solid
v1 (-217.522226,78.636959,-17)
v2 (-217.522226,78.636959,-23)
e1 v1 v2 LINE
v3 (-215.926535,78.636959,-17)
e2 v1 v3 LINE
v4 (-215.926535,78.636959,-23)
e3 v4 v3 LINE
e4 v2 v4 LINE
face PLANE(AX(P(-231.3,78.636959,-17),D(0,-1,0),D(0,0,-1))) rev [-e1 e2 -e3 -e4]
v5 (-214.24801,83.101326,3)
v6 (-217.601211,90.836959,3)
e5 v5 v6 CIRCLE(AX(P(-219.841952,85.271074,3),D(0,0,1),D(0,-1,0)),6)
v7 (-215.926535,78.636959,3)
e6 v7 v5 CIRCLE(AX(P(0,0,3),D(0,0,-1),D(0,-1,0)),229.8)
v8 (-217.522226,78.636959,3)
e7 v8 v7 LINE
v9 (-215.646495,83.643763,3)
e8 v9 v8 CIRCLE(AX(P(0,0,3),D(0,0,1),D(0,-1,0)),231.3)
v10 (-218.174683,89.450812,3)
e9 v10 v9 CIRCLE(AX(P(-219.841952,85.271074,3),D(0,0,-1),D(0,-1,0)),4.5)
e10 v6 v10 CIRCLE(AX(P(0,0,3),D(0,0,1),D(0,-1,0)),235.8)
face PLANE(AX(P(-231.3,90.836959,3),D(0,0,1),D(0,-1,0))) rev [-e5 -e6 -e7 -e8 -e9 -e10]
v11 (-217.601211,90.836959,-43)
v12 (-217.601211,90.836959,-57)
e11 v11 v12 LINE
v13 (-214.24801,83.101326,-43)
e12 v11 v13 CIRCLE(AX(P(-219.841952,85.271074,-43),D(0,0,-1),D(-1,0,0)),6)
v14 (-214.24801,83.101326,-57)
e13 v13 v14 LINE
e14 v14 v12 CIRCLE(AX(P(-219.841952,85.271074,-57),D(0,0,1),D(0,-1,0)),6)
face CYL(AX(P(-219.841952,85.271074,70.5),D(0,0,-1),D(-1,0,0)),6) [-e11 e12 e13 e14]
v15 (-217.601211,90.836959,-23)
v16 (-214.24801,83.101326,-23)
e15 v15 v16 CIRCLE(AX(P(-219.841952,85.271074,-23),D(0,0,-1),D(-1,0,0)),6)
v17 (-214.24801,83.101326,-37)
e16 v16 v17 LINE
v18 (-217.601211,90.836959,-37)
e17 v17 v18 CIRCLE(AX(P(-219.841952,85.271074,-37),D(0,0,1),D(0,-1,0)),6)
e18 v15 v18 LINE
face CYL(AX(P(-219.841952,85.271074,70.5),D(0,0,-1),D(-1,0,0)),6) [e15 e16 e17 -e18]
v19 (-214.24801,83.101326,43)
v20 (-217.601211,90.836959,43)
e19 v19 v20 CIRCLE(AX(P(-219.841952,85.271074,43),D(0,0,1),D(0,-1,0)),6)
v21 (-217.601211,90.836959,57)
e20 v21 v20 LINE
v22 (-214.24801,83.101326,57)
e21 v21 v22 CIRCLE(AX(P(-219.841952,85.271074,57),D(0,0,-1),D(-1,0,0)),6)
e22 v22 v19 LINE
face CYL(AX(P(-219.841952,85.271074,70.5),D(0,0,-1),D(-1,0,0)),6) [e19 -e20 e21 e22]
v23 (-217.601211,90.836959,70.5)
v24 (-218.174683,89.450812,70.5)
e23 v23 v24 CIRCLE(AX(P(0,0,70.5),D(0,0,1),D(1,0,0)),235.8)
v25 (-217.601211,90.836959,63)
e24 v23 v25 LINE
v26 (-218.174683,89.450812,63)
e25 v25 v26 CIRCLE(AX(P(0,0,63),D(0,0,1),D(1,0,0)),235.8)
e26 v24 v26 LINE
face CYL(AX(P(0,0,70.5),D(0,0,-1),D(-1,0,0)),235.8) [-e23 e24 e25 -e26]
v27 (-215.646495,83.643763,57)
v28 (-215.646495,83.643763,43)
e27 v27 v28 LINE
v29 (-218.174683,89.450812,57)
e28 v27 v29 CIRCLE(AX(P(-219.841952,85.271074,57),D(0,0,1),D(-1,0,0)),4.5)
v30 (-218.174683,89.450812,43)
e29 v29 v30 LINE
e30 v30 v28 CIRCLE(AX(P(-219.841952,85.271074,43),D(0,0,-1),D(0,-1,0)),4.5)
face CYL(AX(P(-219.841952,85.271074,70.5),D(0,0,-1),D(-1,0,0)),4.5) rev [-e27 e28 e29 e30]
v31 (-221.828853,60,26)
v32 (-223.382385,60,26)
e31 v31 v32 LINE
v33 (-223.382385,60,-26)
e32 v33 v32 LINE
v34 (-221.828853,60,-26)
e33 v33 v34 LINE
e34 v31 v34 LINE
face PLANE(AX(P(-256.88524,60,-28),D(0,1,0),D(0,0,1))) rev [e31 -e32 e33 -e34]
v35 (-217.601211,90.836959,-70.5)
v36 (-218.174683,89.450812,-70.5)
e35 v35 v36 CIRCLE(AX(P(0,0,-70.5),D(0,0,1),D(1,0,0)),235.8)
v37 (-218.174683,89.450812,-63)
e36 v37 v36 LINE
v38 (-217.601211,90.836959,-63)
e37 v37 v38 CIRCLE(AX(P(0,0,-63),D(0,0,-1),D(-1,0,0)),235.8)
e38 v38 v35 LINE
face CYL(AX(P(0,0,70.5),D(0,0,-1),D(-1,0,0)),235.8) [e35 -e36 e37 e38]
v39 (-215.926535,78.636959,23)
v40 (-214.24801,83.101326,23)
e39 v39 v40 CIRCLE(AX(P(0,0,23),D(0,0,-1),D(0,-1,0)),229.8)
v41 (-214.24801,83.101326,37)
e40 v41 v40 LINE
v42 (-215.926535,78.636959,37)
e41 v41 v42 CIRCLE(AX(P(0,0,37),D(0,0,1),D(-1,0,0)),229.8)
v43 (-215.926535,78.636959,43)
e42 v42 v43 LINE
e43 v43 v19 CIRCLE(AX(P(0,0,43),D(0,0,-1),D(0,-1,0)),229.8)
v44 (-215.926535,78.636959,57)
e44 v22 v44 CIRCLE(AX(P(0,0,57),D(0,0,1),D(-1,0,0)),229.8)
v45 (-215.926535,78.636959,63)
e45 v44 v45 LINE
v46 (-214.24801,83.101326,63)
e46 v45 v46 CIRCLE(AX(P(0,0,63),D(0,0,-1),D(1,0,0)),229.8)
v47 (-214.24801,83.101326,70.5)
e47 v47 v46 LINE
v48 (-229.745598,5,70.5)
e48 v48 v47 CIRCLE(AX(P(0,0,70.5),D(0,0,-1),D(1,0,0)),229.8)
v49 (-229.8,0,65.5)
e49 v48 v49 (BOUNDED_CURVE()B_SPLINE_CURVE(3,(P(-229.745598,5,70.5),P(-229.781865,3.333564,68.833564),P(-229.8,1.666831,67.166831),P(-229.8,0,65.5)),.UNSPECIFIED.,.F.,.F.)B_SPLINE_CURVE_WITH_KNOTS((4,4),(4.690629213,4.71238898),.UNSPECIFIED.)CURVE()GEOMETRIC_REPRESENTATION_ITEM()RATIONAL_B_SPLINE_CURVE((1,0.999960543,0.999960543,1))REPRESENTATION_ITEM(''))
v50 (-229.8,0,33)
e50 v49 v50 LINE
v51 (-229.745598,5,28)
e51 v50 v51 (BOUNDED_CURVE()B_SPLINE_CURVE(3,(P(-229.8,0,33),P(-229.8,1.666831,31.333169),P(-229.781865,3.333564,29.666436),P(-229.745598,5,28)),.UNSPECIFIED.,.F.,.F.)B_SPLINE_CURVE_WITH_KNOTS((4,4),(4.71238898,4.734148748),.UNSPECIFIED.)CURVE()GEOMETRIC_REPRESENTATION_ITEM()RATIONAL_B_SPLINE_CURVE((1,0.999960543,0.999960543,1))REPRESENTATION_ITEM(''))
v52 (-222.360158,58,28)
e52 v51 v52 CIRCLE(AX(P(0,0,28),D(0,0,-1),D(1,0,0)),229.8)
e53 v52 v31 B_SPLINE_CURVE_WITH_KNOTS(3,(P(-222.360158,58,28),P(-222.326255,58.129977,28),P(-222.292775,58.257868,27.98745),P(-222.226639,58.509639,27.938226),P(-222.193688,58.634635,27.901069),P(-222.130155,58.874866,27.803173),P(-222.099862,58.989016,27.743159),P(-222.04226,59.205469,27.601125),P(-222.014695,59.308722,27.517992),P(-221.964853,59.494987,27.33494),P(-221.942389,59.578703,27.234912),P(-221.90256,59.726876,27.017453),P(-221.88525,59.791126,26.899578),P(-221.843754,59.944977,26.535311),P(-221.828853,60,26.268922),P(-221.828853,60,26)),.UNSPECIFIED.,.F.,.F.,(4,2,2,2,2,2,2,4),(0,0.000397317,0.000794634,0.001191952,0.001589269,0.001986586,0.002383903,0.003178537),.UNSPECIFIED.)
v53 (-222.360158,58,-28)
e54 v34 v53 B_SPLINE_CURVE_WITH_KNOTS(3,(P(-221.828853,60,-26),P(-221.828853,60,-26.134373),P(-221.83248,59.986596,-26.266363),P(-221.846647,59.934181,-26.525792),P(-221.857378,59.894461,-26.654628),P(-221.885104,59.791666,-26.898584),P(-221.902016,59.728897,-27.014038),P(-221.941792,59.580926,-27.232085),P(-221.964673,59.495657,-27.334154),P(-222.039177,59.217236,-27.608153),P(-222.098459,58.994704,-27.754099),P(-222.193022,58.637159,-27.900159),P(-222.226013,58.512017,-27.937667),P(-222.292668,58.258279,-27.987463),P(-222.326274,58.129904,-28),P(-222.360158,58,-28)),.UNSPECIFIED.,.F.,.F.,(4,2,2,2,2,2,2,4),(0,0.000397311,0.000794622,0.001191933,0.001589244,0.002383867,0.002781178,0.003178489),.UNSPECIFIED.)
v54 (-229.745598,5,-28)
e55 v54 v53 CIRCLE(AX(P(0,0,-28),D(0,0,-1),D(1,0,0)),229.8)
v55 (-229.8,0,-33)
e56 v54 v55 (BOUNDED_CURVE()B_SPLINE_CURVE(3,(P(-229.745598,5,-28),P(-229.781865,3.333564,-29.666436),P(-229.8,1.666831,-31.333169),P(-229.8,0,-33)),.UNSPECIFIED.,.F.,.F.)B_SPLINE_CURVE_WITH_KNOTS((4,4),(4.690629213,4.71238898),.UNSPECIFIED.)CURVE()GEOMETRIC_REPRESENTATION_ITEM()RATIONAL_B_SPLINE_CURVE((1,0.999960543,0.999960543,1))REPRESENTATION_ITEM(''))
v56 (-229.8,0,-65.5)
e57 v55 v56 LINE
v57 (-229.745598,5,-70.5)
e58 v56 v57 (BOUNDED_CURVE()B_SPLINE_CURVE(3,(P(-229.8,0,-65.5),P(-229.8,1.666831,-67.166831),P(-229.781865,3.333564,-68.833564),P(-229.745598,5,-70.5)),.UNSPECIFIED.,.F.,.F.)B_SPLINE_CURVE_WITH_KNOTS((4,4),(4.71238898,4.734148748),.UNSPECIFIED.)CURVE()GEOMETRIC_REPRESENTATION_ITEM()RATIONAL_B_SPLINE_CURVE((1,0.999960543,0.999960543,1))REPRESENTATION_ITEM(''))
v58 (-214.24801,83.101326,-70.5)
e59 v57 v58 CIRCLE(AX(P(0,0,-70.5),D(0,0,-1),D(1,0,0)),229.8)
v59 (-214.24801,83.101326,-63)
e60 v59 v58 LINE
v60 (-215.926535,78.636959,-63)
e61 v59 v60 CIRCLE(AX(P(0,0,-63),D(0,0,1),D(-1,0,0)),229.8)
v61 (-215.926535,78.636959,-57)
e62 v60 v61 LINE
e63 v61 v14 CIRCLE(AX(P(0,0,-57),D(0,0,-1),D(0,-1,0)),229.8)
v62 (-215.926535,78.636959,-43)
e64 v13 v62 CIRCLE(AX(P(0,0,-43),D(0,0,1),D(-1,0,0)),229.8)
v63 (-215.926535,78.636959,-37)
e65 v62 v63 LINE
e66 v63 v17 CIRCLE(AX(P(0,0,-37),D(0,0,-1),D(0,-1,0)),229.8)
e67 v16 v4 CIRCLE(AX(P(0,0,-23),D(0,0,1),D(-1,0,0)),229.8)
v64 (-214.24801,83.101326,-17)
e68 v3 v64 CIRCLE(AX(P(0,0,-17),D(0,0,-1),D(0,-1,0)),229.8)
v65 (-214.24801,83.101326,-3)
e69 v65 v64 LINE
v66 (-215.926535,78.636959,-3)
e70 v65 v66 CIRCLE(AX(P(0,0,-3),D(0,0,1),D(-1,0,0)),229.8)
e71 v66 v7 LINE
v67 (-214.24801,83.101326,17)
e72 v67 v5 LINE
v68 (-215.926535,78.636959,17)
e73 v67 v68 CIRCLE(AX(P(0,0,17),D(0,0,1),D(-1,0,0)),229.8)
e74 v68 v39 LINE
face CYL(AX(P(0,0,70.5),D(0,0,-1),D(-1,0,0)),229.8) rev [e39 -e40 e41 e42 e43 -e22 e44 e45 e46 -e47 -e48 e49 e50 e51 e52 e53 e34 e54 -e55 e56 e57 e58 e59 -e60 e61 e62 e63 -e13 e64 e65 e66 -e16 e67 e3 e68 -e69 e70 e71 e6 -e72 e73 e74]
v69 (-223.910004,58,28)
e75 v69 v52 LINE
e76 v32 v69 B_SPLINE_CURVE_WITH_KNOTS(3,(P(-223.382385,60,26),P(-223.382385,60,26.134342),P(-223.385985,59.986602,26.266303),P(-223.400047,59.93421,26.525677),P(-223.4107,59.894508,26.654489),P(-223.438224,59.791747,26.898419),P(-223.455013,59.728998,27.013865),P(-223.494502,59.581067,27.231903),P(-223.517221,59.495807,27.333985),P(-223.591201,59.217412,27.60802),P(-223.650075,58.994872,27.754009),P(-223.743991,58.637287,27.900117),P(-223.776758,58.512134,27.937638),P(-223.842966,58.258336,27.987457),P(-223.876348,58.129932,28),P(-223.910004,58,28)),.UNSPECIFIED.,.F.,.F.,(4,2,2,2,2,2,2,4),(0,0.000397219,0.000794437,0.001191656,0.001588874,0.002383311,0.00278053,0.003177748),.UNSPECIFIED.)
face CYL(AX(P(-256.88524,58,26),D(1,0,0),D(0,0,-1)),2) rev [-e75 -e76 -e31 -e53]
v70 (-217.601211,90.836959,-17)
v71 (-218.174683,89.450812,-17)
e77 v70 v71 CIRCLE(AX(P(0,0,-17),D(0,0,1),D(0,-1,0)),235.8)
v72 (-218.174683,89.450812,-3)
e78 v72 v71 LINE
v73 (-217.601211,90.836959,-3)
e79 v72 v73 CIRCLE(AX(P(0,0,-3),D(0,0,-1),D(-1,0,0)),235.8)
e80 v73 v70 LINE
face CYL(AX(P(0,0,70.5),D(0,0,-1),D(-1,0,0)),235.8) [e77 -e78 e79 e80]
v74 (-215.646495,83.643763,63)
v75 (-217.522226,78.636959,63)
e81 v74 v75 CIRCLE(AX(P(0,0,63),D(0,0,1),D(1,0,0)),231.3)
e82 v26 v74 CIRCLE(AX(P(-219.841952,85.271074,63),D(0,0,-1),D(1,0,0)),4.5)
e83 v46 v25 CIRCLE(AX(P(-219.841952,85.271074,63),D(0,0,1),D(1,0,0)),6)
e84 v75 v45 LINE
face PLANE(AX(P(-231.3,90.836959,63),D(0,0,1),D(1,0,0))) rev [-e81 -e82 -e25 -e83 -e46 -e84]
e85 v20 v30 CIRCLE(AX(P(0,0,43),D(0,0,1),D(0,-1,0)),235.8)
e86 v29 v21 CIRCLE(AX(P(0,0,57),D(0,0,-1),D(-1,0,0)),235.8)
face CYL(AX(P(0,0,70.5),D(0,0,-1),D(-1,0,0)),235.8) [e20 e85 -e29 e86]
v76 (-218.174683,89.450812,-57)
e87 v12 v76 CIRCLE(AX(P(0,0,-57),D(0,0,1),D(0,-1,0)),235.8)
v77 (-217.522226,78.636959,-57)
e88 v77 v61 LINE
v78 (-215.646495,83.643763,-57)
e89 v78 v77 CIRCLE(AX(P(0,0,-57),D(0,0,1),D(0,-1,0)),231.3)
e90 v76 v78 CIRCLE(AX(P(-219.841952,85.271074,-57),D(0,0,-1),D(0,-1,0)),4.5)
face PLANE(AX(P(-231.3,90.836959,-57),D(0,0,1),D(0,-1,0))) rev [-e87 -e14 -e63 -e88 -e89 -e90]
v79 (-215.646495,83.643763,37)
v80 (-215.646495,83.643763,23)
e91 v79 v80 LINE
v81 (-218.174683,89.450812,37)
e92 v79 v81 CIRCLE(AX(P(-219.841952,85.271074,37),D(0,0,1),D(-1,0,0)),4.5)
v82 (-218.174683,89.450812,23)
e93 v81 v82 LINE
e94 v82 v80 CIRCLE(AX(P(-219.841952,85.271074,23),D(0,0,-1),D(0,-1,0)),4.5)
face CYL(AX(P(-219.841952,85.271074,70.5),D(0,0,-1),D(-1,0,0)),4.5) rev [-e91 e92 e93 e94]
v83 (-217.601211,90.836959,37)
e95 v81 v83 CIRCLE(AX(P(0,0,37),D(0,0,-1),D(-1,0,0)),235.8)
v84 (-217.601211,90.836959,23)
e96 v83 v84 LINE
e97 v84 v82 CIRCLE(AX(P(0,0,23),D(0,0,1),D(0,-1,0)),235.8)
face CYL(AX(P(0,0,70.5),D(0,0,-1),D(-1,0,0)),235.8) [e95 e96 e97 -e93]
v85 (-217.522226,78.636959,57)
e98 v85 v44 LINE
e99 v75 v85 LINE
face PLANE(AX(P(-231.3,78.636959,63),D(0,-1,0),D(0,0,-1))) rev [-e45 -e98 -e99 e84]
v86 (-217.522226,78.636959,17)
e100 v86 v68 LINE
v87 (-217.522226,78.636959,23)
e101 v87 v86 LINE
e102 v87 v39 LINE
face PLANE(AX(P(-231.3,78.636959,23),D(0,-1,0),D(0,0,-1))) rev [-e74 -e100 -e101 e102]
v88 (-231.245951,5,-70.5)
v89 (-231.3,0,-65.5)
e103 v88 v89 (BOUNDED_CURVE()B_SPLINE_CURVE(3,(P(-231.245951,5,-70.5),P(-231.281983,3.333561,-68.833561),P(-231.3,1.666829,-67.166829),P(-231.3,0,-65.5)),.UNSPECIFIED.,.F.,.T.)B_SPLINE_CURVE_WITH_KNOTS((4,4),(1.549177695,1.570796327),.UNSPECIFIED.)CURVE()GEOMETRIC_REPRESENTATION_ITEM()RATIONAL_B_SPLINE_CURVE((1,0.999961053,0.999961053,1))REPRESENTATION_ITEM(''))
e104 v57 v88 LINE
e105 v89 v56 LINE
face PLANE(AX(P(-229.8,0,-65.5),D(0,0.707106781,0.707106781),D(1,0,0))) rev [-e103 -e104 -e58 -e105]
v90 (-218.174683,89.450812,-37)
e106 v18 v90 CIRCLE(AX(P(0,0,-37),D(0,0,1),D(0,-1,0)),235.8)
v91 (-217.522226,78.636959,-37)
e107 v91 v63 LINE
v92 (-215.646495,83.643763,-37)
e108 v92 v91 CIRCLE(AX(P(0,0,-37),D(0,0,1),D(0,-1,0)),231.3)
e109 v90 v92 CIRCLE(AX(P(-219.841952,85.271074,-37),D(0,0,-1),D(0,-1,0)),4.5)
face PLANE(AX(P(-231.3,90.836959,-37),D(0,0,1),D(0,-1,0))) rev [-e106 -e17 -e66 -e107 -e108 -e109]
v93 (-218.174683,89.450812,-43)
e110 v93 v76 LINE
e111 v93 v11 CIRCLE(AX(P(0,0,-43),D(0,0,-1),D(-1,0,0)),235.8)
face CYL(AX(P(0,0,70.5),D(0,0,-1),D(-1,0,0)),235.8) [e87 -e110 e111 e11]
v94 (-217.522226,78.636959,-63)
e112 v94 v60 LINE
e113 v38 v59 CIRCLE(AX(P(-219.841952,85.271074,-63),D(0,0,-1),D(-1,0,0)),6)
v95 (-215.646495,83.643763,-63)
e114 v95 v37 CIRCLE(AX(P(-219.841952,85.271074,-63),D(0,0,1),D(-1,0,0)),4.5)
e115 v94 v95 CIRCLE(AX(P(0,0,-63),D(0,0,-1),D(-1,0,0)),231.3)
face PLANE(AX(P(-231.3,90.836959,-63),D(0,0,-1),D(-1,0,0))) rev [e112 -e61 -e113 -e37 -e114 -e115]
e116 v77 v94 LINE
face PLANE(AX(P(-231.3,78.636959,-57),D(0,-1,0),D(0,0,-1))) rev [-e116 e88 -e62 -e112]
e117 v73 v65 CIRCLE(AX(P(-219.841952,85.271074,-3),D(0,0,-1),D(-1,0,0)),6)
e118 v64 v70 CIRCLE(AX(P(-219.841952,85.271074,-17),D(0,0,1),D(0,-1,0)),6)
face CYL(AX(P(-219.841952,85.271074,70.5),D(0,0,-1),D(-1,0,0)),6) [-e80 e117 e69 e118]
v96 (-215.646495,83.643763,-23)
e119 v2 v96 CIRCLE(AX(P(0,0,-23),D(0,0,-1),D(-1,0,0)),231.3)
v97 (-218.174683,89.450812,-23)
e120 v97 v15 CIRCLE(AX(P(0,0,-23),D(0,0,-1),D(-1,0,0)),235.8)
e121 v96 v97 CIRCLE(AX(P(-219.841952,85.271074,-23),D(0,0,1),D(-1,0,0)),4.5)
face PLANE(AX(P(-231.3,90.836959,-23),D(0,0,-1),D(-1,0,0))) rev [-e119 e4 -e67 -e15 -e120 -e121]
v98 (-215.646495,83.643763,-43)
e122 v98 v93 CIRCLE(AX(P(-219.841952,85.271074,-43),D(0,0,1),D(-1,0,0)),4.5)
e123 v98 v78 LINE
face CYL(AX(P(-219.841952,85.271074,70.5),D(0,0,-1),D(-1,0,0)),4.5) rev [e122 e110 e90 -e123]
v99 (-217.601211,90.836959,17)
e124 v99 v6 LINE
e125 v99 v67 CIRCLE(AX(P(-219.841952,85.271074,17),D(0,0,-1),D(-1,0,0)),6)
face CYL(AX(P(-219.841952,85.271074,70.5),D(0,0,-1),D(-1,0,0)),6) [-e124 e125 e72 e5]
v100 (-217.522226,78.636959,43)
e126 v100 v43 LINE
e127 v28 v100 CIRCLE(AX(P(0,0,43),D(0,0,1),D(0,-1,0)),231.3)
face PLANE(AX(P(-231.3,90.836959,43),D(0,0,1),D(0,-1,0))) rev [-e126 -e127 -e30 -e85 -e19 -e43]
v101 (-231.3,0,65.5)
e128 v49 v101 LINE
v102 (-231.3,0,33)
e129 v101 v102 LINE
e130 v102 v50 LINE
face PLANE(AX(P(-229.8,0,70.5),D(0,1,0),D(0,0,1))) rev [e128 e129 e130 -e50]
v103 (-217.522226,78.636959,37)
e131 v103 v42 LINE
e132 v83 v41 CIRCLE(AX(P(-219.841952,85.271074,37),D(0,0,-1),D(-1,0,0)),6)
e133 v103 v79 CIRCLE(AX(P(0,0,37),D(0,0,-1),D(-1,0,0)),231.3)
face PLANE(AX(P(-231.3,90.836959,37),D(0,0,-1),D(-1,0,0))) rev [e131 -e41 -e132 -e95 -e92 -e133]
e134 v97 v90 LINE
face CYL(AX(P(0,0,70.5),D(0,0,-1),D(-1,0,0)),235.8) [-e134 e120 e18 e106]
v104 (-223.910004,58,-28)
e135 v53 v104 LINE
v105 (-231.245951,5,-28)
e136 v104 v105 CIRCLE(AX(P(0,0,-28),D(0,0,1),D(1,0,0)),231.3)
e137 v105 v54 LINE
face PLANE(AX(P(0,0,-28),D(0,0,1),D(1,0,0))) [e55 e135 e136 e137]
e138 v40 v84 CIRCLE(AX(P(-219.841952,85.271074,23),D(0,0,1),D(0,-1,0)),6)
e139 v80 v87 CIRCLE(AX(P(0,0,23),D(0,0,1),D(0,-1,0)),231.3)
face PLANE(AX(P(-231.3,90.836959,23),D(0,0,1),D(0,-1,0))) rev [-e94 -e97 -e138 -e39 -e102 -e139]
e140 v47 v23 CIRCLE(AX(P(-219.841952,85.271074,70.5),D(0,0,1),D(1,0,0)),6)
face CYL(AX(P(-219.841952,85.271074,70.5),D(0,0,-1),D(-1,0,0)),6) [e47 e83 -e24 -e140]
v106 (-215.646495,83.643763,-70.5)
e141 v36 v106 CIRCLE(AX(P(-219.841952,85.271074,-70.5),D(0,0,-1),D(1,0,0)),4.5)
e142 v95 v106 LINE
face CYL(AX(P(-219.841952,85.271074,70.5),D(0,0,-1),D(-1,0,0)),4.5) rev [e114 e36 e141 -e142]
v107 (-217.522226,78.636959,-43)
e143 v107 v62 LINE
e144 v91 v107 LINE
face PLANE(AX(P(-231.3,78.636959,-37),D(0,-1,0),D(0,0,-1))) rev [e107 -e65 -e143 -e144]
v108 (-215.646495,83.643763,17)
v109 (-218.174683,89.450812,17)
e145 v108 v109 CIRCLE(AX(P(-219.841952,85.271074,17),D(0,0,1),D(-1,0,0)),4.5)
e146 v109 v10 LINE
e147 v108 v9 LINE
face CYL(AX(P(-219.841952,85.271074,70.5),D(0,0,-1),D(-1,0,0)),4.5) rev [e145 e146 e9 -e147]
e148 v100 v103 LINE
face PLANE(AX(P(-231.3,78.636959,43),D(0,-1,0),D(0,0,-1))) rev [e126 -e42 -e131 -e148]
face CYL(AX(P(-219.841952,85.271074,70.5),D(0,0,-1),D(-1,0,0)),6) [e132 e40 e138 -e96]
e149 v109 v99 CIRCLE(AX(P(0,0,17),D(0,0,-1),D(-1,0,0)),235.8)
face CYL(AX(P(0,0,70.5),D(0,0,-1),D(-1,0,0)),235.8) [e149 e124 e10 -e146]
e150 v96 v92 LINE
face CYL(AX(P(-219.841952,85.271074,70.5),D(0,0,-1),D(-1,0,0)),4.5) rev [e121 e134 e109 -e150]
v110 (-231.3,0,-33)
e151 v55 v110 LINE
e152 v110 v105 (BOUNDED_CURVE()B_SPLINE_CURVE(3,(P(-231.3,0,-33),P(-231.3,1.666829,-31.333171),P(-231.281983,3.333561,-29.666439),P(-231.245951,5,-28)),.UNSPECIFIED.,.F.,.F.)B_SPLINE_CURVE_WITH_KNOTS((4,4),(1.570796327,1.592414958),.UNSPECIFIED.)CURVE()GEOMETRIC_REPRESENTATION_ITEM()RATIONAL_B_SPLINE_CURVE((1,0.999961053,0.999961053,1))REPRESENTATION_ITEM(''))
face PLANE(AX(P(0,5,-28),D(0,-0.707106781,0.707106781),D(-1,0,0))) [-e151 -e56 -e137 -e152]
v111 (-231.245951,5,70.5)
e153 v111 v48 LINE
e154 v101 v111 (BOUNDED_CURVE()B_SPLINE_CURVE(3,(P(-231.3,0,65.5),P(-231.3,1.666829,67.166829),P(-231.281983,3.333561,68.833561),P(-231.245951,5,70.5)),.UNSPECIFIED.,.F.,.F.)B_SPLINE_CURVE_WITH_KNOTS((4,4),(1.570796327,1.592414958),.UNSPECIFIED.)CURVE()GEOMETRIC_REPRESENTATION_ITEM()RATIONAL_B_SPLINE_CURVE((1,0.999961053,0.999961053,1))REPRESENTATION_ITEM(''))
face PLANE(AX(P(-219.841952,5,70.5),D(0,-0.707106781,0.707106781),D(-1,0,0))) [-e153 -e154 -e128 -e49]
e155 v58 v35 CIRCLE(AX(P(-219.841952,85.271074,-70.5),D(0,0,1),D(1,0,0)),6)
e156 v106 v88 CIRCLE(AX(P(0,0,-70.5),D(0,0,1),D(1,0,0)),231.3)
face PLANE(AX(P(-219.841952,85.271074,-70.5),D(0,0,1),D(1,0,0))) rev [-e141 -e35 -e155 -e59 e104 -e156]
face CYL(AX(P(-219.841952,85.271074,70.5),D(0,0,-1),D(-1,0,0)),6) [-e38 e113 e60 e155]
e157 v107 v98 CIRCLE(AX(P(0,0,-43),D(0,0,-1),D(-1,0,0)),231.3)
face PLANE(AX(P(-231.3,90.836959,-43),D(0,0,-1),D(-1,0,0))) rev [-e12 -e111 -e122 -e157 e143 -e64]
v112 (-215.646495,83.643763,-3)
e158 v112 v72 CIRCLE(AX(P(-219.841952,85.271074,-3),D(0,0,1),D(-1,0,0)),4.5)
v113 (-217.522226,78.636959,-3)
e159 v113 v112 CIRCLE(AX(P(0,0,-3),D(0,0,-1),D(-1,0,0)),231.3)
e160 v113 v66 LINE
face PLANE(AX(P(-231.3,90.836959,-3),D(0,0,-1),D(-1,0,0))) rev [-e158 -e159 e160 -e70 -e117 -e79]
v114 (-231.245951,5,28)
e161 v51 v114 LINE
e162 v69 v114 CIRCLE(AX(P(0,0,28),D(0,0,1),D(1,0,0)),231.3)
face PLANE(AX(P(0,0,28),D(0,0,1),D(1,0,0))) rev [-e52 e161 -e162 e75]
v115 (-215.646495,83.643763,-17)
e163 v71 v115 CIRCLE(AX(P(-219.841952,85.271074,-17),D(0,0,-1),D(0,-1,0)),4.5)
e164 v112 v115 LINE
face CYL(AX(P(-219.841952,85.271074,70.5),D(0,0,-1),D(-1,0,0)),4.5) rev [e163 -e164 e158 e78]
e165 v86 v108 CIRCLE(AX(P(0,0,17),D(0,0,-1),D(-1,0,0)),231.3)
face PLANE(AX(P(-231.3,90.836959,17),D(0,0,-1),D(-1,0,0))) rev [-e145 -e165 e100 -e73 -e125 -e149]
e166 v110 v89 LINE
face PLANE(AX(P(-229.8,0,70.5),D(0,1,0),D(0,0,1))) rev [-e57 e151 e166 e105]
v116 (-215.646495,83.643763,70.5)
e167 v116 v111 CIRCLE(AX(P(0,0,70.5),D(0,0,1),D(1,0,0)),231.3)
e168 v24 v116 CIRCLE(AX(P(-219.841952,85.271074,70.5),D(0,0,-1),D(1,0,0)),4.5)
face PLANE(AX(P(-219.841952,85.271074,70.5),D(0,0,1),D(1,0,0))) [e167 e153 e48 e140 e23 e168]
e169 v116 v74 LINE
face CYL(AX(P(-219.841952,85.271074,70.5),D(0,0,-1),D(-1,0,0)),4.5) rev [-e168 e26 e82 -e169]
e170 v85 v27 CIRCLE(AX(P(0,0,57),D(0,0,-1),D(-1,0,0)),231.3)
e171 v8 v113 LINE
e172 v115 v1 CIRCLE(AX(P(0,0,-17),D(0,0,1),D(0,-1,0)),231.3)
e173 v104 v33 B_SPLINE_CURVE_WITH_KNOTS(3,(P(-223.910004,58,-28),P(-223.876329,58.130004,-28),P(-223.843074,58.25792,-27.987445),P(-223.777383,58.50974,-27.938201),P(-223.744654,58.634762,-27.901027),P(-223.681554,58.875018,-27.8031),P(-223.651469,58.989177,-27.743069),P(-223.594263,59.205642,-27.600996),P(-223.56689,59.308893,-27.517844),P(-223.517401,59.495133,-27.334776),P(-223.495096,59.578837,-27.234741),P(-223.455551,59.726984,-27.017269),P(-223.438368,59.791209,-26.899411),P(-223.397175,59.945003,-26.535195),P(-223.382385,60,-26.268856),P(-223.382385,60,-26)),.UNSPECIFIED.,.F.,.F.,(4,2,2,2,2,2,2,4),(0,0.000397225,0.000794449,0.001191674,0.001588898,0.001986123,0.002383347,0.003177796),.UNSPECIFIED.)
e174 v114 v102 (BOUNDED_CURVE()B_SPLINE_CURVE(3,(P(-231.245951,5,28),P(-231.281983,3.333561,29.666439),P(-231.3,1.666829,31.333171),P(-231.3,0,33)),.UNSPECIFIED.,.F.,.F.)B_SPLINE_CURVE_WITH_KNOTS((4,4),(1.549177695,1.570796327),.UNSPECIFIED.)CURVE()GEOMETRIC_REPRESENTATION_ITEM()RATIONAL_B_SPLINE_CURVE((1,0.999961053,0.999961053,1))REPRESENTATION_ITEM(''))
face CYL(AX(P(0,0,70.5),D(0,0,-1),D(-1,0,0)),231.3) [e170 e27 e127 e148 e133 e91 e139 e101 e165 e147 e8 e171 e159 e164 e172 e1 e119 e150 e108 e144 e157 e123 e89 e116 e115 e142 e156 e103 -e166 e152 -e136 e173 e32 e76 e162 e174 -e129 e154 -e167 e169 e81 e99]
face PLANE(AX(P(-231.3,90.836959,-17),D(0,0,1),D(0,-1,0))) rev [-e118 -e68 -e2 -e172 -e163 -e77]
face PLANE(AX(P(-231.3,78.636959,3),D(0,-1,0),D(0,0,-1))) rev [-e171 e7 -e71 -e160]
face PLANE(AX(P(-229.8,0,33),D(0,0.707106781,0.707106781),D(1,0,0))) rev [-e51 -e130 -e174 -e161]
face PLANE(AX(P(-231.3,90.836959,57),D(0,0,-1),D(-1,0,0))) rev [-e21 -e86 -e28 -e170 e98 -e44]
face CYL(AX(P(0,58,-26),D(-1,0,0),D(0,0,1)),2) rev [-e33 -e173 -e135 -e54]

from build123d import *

# Parameters (mm, degrees)
BOSS_EXTRUDE1_DEPTH = 70.5
SKETCH2_W           = 62.190757718
SKETCH2_H           = 82.229138737
CUT_EXTRUDE1_DEPTH  = 28
FILLET1_R           = 2
CHAMFER2_SIZE       = 5
SKETCH3_W           = 6
SKETCH3_H           = 12.2
CUT_EXTRUDE2_DEPTH  = 259.304651789


with BuildPart() as part:
    # Sketch1 → Boss-Extrude1 (new, symmetric)
    with BuildSketch(Plane.XY):
        with BuildLine():
            Line((-229.8, 0), (-231.3, 0))
            ThreePointArc((-231.3, 0), (-227.352946258, 42.547947397), (-215.646495221, 83.64376306))
            ThreePointArc((-215.646495221, 83.64376306), (-215.716016682, 87.067362872), (-218.174682858, 89.450811957))
            ThreePointArc((-218.174682858, 89.450811957), (-217.889049095, 90.144341388), (-217.601210761, 90.836958751))
            ThreePointArc((-217.601210761, 90.836958751), (-214.336902597, 87.65737358), (-214.248009519, 83.101326205))
            ThreePointArc((-214.248009519, 83.101326205), (-225.878543235, 42.272020371), (-229.8, 0))
        make_face()
    extrude(amount=BOSS_EXTRUDE1_DEPTH, both=True)

    # Sketch2 → Cut-Extrude1 (cut, symmetric)
    with BuildSketch(Plane.XY):
        with Locations((-225.789861071, 18.885430632)):
            Rectangle(SKETCH2_W, SKETCH2_H)
    extrude(amount=CUT_EXTRUDE1_DEPTH, both=True, mode=Mode.SUBTRACT)

    # Fillet1
    fillet1_edges = [part.edges().sort_by_distance(p)[0] for p in [
        (-222.605619054, 60, -28),
        (-222.605619054, 60, 28),
    ]]
    fillet(fillet1_edges, radius=FILLET1_R)

    # Chamfer2
    chamfer2_edges = [part.edges().sort_by_distance(p)[0] for p in [
        (-230.55, 0, 70.5),
        (-230.55, 0, 28),
        (-230.55, 0, -28),
        (-230.55, 0, -70.5),
    ]]
    chamfer(chamfer2_edges, length=CHAMFER2_SIZE)

    # Sketch3 → Cut-Extrude2 (cut, through all)
    with BuildSketch(Plane(origin=(0, 0, 0), x_dir=(0, 0, -1), z_dir=(1, 0, 0))):
        with Locations((60, 84.736958751)):
            Rectangle(SKETCH3_W, SKETCH3_H)
        with Locations((40, 84.736958751)):
            Rectangle(SKETCH3_W, SKETCH3_H)
        with Locations((20, 84.736958751)):
            Rectangle(SKETCH3_W, SKETCH3_H)
        with Locations((0, 84.736958751)):
            Rectangle(SKETCH3_W, SKETCH3_H)
        with Locations((-20, 84.736958751)):
            Rectangle(SKETCH3_W, SKETCH3_H)
        with Locations((-40, 84.736958751)):
            Rectangle(SKETCH3_W, SKETCH3_H)
        with Locations((-60, 84.736958751)):
            Rectangle(SKETCH3_W, SKETCH3_H)
    extrude(amount=-CUT_EXTRUDE2_DEPTH, mode=Mode.SUBTRACT)


solid = part.part
